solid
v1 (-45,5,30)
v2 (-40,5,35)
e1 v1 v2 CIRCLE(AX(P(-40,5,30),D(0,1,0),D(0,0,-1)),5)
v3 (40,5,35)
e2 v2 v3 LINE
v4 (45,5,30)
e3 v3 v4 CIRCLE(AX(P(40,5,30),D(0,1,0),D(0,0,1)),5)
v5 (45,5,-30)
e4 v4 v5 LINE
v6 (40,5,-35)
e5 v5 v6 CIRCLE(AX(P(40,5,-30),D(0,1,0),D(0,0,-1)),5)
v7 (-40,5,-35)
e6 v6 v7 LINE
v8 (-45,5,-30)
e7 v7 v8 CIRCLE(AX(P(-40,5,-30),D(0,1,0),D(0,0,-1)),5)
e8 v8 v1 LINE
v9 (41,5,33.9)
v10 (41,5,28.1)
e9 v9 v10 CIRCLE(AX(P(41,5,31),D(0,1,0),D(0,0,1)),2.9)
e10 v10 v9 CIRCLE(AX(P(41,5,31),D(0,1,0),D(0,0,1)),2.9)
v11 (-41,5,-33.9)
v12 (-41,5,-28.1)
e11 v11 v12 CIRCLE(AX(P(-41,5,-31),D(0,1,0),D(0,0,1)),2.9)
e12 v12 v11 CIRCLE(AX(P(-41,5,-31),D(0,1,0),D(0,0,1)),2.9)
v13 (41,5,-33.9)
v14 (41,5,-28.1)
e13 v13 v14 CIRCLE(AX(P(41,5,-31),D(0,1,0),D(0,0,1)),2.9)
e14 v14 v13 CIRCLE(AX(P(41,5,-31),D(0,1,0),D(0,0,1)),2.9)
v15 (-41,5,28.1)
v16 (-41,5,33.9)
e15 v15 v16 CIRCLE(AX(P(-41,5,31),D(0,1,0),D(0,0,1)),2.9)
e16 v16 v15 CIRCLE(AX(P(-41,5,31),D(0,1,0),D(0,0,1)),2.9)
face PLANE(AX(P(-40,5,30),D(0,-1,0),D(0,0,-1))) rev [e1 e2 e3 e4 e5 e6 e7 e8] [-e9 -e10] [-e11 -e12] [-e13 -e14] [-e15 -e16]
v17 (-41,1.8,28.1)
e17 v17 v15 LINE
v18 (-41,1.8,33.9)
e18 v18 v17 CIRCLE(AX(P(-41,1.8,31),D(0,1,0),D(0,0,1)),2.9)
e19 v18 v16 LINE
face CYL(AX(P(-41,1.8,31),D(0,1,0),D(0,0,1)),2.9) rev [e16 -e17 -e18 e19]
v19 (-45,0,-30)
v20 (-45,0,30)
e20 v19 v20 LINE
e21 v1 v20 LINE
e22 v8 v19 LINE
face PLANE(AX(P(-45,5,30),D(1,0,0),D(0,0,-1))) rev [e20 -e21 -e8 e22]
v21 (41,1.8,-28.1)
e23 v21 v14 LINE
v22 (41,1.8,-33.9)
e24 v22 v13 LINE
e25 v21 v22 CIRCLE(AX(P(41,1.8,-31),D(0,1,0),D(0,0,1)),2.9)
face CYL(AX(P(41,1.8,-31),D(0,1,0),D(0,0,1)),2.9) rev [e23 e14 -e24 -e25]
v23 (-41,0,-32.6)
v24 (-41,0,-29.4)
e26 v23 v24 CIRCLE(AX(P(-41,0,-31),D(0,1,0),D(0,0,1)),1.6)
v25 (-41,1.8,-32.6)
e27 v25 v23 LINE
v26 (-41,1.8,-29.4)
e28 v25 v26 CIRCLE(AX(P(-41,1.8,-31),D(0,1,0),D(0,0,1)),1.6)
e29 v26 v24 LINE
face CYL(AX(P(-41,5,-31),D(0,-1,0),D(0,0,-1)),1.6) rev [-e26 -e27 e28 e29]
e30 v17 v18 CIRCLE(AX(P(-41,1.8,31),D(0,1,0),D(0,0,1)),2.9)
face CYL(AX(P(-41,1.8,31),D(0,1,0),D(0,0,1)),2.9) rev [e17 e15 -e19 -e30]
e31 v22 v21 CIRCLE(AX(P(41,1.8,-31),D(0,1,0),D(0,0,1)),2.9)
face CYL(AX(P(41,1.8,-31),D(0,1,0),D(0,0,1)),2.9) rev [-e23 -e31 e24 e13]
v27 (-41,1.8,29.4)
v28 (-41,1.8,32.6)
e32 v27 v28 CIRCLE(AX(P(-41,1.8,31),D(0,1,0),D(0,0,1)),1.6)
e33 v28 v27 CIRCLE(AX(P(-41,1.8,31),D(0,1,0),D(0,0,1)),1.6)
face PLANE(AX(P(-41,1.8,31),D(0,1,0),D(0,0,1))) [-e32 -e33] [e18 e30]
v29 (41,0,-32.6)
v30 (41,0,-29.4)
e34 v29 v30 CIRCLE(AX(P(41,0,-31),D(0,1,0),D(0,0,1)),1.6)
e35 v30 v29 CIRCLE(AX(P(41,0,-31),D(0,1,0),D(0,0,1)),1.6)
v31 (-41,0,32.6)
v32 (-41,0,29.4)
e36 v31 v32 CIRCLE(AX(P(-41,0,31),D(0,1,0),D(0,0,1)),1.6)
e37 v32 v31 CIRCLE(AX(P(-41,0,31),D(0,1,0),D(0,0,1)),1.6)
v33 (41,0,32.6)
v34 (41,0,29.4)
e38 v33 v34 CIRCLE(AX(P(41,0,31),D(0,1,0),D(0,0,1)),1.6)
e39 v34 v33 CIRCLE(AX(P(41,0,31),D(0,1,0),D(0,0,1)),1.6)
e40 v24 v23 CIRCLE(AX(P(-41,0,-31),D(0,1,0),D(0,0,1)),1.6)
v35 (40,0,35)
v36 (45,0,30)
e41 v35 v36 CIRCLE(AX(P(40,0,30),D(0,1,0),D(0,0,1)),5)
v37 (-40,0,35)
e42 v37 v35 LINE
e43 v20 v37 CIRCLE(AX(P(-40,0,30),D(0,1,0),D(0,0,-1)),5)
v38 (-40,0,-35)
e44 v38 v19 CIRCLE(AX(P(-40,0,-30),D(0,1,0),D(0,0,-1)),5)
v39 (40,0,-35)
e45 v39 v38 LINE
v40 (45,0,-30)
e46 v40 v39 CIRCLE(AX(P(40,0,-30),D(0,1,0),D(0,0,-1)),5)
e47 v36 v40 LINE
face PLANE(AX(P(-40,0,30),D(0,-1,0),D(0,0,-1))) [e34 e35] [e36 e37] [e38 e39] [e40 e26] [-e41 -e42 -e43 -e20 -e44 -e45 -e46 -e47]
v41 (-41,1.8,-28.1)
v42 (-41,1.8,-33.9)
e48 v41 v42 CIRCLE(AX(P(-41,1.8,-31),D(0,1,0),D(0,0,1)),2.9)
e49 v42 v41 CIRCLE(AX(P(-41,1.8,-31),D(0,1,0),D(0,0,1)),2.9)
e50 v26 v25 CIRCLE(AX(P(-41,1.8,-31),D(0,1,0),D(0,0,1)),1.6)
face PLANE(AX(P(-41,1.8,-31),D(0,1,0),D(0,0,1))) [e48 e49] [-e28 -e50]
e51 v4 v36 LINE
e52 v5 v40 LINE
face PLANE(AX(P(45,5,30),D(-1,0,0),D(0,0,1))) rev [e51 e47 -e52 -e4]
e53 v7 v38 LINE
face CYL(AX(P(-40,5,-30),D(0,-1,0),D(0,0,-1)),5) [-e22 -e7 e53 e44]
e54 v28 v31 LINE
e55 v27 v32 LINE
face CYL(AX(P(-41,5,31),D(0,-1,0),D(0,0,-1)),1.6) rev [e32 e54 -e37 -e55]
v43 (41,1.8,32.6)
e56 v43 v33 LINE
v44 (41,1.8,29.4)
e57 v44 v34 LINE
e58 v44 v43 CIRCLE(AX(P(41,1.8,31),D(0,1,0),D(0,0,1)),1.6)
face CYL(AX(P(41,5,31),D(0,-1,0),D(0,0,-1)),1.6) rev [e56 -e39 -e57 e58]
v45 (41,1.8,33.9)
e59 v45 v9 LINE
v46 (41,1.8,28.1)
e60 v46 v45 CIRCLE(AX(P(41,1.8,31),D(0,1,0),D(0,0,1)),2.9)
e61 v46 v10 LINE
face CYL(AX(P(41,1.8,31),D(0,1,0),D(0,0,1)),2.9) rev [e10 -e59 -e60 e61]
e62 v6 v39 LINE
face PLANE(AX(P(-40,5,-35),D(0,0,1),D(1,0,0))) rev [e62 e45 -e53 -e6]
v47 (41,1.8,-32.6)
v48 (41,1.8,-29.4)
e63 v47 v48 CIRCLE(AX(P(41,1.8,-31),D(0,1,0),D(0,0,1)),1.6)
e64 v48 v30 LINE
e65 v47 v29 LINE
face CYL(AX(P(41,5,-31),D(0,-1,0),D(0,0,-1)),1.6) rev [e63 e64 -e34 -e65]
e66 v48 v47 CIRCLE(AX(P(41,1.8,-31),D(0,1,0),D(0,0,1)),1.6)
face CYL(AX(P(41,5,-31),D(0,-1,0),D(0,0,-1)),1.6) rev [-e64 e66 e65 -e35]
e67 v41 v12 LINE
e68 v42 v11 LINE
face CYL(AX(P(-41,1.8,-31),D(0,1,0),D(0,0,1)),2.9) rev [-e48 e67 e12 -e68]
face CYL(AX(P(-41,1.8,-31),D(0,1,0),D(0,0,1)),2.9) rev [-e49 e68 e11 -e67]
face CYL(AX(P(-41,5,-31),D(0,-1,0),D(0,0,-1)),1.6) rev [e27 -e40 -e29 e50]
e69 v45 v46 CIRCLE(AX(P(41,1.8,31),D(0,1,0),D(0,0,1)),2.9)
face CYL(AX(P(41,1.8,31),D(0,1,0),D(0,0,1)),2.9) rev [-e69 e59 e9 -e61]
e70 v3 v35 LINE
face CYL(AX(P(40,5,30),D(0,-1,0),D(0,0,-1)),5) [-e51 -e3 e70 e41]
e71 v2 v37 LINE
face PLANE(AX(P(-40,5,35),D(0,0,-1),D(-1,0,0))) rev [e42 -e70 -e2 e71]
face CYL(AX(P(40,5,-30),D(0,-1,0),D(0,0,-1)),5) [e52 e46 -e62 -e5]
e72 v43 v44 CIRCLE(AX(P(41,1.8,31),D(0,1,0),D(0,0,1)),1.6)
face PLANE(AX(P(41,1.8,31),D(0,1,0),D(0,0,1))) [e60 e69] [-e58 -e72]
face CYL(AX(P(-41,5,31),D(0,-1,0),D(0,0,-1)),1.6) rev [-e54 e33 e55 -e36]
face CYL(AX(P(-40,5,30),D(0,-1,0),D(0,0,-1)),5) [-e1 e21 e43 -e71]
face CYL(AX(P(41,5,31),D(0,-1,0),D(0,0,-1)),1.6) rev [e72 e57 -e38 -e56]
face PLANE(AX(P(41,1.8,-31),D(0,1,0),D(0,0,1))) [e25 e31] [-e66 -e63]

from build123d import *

# Parameters (mm, degrees)
SKETCH1_R           = 1.6
BOSS_EXTRUDE1_DEPTH = 5
SKETCH2_R           = 2.9
CUT_EXTRUDE1_DEPTH  = 3.2


with BuildPart() as part:
    # Sketch1 → Boss-Extrude1 (new body)
    with BuildSketch(Plane(origin=(0, 0, 0), x_dir=(1, 0, 0), z_dir=(0, 1, 0))):
        with BuildLine():
            Line((-40, -35), (40, -35))
            ThreePointArc((40, -35), (43.535533906, -33.535533906), (45, -30))
            Line((45, -30), (45, 30))
            ThreePointArc((45, 30), (43.535533906, 33.535533906), (40, 35))
            Line((40, 35), (-40, 35))
            ThreePointArc((-40, 35), (-43.535533906, 33.535533906), (-45, 30))
            Line((-45, 30), (-45, -30))
            ThreePointArc((-45, -30), (-43.535533906, -33.535533906), (-40, -35))
        make_face()
        with Locations(Location((-41, 31, 0), (0, 0, 270))):
            Circle(SKETCH1_R, mode=Mode.SUBTRACT)
        with Locations(Location((-41, -31, 0), (0, 0, 270))):
            Circle(SKETCH1_R, mode=Mode.SUBTRACT)
        with Locations(Location((41, -31, 0), (0, 0, 270))):
            Circle(SKETCH1_R, mode=Mode.SUBTRACT)
        with Locations(Location((41, 31, 0), (0, 0, 270))):
            Circle(SKETCH1_R, mode=Mode.SUBTRACT)
    extrude(amount=BOSS_EXTRUDE1_DEPTH)

    # Sketch2 → Cut-Extrude1 (cut)
    with BuildSketch(Plane(origin=(0, 5, 0), x_dir=(1, 0, 0), z_dir=(0, 1, 0))):
        with Locations(Location((41, 31, 0), (0, 0, 270))):
            Circle(SKETCH2_R)
        with Locations(Location((-41, 31, 0), (0, 0, 270))):
            Circle(SKETCH2_R)
        with Locations(Location((-41, -31, 0), (0, 0, 270))):
            Circle(SKETCH2_R)
        with Locations(Location((41, -31, 0), (0, 0, 270))):
            Circle(SKETCH2_R)
    extrude(amount=-CUT_EXTRUDE1_DEPTH, mode=Mode.SUBTRACT)


solid = part.part
